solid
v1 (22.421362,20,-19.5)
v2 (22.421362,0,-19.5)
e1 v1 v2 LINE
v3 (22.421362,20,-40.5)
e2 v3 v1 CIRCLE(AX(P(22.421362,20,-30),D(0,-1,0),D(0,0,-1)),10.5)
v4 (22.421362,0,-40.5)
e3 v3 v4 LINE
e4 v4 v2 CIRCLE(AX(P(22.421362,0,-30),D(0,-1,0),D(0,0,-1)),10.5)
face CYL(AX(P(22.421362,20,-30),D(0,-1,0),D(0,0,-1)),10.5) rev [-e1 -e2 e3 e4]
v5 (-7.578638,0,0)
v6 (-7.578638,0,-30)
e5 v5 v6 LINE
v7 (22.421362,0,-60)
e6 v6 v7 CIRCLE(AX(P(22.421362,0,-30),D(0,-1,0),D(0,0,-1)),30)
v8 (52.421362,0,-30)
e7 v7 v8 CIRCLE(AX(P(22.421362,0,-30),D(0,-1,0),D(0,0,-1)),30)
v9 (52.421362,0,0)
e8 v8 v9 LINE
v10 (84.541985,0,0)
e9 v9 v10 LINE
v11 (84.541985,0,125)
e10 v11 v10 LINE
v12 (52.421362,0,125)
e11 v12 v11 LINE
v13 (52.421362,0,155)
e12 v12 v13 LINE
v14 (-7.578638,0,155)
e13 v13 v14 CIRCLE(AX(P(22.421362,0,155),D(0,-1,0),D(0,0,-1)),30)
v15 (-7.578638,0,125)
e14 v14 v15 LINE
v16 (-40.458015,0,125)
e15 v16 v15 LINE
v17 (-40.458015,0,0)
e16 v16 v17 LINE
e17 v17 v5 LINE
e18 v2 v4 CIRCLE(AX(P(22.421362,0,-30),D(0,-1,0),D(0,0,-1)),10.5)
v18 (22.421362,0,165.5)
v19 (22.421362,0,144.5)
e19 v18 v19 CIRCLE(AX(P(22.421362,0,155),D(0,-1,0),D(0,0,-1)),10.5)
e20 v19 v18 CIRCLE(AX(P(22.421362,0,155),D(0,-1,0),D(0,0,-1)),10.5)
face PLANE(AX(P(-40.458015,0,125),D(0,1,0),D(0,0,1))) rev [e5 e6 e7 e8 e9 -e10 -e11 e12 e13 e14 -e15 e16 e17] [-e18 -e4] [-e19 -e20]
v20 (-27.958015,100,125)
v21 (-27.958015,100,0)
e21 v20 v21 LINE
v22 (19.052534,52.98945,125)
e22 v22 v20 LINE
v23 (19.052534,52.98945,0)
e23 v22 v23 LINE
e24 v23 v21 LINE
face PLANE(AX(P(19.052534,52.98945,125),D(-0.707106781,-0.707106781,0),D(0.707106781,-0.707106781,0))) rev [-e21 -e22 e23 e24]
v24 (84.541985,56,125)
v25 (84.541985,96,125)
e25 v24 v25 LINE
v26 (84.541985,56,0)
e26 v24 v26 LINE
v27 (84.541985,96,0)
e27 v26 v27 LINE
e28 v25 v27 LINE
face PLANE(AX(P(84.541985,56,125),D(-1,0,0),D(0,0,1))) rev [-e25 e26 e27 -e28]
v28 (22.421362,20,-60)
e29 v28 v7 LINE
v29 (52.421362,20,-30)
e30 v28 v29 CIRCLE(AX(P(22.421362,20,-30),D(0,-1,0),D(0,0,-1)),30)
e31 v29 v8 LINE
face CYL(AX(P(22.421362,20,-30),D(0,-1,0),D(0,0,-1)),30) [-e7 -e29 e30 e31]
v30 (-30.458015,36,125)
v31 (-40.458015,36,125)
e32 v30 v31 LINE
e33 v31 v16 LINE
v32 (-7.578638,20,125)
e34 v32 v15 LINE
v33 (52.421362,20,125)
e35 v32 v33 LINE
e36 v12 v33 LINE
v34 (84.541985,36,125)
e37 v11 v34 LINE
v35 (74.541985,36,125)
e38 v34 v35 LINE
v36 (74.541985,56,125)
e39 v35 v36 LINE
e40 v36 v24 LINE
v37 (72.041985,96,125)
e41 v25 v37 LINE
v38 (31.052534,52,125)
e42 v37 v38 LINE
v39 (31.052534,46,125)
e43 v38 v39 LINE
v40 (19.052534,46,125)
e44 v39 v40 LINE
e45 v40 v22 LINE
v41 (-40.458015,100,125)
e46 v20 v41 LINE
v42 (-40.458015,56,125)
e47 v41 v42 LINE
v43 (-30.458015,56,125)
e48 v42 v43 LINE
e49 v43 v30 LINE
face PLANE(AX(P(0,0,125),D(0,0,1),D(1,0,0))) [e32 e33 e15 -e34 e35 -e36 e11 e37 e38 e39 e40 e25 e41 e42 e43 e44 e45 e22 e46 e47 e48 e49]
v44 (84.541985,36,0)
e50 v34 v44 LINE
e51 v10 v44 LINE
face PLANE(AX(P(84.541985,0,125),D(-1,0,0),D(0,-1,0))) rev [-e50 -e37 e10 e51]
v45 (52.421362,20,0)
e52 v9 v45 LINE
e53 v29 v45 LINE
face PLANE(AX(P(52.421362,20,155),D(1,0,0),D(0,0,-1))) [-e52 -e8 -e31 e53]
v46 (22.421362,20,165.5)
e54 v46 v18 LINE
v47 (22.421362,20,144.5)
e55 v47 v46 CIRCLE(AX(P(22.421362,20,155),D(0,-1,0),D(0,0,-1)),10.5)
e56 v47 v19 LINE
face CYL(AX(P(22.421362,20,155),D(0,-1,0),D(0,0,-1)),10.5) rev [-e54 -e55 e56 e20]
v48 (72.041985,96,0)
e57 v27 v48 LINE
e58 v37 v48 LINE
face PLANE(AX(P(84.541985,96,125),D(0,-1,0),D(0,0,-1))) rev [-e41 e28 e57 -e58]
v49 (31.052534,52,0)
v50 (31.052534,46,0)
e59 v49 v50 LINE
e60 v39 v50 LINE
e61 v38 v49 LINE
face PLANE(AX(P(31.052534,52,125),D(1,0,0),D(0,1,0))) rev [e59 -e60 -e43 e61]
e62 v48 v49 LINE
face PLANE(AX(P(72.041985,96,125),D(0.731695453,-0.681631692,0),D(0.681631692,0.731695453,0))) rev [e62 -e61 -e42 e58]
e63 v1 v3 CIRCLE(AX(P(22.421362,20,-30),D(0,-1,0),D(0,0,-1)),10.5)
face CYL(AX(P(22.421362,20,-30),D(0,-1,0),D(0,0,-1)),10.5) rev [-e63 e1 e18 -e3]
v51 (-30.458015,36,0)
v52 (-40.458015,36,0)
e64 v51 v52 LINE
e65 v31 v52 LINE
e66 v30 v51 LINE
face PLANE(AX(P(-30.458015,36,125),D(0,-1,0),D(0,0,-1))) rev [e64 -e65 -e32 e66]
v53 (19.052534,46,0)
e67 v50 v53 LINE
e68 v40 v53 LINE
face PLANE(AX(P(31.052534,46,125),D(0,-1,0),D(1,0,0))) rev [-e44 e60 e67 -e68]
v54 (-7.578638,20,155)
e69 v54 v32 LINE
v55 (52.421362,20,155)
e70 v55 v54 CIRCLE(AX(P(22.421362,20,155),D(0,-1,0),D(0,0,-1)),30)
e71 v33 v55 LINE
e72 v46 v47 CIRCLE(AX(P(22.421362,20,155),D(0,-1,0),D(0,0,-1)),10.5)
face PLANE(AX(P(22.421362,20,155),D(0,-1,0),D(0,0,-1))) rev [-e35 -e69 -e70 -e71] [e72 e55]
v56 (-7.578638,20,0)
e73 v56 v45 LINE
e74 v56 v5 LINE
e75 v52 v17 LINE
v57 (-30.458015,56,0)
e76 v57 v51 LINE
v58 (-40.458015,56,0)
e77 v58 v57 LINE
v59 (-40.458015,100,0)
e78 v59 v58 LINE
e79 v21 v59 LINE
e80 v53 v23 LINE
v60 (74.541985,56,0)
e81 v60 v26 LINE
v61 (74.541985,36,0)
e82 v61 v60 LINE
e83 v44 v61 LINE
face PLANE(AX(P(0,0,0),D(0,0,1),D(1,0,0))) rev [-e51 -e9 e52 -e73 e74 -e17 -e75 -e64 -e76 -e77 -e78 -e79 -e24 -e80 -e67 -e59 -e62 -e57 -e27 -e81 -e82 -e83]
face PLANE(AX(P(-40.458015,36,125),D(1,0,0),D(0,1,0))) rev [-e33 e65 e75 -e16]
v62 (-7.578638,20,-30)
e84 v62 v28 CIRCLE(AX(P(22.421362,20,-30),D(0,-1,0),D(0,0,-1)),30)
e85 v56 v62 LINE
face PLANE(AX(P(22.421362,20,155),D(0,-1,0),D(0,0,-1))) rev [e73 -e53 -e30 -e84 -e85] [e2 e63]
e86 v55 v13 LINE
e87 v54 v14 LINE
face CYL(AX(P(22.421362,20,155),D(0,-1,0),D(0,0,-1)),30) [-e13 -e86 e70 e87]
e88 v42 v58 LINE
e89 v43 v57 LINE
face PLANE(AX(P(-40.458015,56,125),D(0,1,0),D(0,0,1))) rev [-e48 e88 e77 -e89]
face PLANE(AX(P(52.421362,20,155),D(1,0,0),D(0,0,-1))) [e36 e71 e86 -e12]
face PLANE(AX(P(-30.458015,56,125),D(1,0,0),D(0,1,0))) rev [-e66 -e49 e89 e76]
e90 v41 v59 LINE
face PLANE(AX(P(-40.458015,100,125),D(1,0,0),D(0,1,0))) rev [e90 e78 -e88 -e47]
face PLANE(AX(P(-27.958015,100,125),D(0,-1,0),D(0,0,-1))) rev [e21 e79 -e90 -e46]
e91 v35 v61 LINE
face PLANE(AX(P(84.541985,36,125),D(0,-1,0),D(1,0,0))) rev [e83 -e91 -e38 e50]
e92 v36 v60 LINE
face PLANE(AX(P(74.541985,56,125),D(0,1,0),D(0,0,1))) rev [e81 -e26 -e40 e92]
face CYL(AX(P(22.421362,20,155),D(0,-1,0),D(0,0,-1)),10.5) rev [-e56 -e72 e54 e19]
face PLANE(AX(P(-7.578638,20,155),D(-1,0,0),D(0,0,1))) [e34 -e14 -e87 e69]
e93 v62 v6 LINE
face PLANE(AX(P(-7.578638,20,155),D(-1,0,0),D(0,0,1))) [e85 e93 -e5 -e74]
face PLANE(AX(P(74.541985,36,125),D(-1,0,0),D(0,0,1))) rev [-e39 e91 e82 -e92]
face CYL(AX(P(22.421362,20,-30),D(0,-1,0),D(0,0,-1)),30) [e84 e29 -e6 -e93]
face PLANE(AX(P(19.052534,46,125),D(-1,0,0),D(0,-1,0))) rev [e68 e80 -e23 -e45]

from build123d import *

# Parameters (mm, degrees)
V_BLOCK_BODY_DEPTH     = 125
MOUNTING_LUGS_SKETCH_R = 10.5
MOUNTING_LUGS_DEPTH    = 20


with BuildPart() as part:
    # V-Block Profile Sketch → V-Block Body (new body)
    with BuildSketch(Plane.XY):
        Polygon((-40.458015267, 0), (84.541984733, 0), (84.541984733, 36), (74.541984733, 36), (74.541984733, 56), (84.541984733, 56), (84.541984733, 96), (72.041984733, 96), (31.052534351, 52), (31.052534351, 46), (19.052534351, 46), (19.052534351, 52.989450382), (-27.958015267, 100), (-40.458015267, 100), (-40.458015267, 56), (-30.458015267, 56), (-30.458015267, 36), (-40.458015267, 36), align=None)
    extrude(amount=V_BLOCK_BODY_DEPTH)

    # Mounting Lugs Sketch → Mounting Lugs (add)
    with BuildSketch(Plane.XZ):
        with BuildLine():
            Line((52.421361688, 155), (52.421361688, -30))
            ThreePointArc((52.421361688, -30), (22.421361688, -60), (-7.578638312, -30))
            Line((-7.578638312, -30), (-7.578638312, 155))
            ThreePointArc((-7.578638312, 155), (22.421361688, 185), (52.421361688, 155))
        make_face()
        with Locations(Location((22.421361688, 155, 0), (0, 0, 270))):
            Circle(MOUNTING_LUGS_SKETCH_R, mode=Mode.SUBTRACT)
        with Locations(Location((22.421361688, -30, 0), (0, 0, 270))):
            Circle(MOUNTING_LUGS_SKETCH_R, mode=Mode.SUBTRACT)
    extrude(amount=-MOUNTING_LUGS_DEPTH)


solid = part.part
